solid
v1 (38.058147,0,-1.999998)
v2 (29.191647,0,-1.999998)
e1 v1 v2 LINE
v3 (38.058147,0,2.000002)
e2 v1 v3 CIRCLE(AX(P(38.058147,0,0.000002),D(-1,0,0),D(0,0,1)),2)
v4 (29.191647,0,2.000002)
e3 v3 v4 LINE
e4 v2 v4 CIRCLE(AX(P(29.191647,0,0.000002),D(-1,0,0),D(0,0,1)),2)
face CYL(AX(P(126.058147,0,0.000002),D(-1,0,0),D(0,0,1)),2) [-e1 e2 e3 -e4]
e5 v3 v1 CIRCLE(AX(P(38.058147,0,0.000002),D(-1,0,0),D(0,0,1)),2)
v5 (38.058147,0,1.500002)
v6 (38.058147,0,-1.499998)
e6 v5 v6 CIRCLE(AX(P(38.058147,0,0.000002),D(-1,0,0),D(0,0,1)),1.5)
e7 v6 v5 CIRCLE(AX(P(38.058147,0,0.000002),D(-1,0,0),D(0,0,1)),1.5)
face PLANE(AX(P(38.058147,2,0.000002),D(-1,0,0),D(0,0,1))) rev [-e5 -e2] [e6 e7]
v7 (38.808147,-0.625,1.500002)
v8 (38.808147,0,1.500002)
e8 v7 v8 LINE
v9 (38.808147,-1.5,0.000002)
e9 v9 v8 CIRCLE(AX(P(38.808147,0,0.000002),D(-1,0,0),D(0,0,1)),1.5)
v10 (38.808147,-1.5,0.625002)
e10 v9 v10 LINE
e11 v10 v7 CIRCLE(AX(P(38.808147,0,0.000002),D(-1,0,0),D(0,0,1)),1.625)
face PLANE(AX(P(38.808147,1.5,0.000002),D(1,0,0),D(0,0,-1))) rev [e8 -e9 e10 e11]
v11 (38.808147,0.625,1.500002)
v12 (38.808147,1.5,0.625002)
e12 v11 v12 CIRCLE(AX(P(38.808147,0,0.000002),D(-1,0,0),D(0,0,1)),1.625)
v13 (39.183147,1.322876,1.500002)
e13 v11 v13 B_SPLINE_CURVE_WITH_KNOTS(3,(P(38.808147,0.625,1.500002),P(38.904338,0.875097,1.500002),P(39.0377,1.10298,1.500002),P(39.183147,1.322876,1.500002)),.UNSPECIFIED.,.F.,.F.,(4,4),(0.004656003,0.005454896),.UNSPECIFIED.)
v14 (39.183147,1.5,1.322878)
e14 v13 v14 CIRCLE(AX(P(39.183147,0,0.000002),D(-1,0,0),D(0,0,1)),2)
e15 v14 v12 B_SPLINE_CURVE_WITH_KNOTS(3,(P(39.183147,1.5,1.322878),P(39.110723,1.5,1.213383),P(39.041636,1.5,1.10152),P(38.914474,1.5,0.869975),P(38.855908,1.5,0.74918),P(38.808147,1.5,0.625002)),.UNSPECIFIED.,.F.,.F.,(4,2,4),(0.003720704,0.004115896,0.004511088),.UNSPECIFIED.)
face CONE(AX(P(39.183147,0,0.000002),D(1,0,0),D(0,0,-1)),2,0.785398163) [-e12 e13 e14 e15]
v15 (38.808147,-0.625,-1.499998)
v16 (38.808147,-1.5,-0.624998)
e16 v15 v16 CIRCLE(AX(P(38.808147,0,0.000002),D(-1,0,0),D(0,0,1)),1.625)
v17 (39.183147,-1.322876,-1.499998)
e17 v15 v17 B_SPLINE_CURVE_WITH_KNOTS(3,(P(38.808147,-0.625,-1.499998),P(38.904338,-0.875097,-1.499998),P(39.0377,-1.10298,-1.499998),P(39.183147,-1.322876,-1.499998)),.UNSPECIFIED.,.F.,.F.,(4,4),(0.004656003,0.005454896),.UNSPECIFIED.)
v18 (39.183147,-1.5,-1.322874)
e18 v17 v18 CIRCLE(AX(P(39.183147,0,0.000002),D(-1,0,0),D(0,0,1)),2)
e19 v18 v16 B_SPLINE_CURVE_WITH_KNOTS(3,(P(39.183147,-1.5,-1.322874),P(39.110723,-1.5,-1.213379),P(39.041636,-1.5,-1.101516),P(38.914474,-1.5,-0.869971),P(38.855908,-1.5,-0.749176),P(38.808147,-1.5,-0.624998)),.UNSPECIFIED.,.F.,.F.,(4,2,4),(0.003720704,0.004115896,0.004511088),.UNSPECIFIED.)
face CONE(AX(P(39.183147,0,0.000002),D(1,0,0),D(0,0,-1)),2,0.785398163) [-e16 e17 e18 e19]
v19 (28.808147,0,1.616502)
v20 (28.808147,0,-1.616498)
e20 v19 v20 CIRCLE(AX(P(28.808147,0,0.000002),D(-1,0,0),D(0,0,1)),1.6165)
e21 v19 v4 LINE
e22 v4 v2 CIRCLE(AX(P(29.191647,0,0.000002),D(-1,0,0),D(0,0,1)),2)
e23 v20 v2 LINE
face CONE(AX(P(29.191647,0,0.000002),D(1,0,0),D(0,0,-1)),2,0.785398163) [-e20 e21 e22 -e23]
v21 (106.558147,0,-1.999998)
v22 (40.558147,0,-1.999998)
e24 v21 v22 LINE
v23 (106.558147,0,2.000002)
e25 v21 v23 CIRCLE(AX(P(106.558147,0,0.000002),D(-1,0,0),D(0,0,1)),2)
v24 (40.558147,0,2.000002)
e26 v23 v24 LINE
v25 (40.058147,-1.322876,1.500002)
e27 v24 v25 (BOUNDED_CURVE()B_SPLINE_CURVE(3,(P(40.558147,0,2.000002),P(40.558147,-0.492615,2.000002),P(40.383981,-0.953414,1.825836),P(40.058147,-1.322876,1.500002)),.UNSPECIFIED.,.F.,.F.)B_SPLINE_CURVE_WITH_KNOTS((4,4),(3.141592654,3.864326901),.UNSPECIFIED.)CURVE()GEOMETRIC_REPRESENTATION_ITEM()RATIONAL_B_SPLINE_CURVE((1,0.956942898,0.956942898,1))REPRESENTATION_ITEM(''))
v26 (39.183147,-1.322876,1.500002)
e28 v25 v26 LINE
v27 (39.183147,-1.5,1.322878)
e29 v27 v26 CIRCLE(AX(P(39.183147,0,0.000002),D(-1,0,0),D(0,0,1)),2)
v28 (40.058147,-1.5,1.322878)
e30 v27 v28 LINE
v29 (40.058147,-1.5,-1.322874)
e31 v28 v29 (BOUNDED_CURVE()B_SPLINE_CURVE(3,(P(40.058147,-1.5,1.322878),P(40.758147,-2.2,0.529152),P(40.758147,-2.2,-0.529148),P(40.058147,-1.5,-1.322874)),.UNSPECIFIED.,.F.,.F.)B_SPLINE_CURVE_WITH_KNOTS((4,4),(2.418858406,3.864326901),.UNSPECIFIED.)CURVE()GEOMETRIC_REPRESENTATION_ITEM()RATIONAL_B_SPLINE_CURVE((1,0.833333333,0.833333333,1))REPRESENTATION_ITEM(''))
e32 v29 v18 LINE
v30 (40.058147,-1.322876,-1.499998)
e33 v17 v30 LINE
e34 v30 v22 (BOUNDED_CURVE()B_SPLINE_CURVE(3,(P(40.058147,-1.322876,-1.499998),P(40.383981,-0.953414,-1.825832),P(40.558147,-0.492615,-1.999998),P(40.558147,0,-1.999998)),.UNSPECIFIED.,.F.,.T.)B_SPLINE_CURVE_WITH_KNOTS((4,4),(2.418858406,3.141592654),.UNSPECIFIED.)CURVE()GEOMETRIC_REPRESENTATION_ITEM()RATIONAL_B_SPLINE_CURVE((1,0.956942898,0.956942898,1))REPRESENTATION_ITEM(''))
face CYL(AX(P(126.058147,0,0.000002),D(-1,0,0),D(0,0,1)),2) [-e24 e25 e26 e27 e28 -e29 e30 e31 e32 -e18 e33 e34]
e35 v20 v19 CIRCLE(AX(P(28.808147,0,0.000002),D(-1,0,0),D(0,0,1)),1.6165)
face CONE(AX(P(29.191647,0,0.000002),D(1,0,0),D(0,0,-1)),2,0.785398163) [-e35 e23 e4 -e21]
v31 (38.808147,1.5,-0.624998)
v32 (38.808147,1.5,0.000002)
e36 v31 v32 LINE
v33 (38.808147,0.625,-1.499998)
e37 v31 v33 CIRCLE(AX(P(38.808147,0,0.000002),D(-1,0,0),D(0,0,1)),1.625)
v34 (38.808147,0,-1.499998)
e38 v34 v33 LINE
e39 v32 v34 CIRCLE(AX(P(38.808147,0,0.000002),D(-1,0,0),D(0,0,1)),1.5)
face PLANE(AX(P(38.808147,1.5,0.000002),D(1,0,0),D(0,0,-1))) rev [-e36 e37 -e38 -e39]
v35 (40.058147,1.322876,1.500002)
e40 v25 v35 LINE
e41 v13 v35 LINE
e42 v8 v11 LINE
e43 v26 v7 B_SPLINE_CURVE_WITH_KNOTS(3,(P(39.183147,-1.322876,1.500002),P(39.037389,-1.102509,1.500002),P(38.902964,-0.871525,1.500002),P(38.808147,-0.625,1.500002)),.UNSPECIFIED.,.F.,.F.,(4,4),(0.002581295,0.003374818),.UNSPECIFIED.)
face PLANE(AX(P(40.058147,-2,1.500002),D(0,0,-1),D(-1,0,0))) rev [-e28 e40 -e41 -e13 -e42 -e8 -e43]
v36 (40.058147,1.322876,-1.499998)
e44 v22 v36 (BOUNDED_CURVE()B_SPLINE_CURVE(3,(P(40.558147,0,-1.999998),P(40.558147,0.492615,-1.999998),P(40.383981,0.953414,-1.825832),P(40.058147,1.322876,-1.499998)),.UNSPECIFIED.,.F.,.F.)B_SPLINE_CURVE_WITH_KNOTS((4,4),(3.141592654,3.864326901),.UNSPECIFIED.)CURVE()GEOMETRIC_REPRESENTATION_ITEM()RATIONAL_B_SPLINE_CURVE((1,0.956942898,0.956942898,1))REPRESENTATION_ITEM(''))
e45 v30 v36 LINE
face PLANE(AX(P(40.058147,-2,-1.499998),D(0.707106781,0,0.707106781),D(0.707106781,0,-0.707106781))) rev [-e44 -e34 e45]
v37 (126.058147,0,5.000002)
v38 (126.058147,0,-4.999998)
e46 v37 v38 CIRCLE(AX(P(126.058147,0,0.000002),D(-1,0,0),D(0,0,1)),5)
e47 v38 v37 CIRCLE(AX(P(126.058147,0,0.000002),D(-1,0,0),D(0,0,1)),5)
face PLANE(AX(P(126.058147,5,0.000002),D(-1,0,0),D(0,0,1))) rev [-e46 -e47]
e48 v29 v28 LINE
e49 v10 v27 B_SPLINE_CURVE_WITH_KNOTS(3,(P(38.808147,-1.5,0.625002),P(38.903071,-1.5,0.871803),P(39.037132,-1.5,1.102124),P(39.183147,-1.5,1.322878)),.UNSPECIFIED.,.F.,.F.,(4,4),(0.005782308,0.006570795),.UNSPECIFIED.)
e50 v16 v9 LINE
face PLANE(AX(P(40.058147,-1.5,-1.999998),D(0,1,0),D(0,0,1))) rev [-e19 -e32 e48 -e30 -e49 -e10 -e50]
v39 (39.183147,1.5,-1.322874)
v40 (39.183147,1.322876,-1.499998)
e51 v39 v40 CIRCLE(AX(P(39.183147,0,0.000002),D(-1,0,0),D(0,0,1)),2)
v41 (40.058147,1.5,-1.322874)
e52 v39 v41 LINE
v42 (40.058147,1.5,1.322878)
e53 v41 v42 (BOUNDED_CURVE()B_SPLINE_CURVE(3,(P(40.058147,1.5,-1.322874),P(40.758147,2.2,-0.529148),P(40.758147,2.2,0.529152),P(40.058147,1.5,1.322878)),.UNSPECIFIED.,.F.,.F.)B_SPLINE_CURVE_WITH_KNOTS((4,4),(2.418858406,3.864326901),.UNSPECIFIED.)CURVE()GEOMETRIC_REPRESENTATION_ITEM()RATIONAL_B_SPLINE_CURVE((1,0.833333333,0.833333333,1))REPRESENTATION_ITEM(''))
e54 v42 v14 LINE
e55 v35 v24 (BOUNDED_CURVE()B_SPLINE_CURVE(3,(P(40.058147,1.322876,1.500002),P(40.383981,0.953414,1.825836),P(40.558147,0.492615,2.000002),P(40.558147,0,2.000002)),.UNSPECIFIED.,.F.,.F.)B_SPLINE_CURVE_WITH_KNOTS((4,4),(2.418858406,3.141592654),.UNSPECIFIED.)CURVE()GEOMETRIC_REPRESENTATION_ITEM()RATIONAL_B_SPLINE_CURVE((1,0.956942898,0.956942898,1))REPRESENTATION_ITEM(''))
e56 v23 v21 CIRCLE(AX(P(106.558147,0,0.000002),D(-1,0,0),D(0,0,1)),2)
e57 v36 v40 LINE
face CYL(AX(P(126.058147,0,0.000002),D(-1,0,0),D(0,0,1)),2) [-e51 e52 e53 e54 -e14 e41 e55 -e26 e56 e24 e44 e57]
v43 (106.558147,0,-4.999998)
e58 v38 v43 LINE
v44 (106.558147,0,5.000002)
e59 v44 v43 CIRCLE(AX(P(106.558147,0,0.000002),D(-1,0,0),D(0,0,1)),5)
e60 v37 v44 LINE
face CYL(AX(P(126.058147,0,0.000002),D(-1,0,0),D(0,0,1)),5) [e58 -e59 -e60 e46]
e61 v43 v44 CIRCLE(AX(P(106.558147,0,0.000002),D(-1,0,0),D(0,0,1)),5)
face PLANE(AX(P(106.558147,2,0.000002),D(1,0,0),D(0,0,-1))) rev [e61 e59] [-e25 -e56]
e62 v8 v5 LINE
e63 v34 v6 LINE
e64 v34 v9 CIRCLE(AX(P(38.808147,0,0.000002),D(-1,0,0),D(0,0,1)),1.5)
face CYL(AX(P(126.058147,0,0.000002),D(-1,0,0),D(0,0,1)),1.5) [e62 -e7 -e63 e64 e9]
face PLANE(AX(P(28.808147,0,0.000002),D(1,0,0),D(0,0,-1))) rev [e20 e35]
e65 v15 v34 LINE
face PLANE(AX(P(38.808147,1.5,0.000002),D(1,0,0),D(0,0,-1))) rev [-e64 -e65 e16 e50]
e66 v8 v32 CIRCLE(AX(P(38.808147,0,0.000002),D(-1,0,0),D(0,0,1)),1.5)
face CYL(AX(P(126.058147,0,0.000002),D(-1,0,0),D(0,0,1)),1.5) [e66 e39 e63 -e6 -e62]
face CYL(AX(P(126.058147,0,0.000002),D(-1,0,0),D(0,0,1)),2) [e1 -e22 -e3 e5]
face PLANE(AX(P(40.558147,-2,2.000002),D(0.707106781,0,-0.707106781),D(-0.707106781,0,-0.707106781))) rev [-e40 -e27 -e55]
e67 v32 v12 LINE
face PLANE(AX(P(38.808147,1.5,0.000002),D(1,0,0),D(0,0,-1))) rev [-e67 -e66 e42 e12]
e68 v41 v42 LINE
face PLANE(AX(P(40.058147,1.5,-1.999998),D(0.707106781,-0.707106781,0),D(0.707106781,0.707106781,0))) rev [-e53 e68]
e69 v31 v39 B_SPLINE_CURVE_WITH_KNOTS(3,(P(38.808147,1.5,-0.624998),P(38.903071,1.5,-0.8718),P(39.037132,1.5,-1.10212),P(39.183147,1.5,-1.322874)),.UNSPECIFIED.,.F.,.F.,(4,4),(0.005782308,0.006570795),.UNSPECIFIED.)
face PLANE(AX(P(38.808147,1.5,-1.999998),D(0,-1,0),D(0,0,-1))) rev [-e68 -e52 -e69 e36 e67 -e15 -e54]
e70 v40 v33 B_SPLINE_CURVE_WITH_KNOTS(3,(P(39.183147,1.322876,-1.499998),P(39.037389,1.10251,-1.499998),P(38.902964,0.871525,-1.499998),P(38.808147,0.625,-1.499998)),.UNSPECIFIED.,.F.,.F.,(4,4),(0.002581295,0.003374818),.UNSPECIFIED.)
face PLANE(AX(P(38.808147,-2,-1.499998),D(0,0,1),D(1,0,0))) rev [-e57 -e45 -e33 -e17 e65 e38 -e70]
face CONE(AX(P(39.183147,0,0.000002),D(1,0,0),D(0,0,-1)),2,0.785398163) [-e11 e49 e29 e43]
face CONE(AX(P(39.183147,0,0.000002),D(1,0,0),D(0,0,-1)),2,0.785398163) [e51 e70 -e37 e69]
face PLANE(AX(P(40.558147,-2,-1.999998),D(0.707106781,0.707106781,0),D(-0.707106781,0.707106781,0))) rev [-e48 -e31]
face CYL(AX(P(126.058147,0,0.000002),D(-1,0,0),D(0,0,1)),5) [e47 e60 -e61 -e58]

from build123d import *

# Parameters (mm, degrees)
CUT_EXTRUDE_1_DEPTH      = 4
CUT_EXTRUDE_1_DEPTH_BACK = 4
CUT_EXTRUDE_2_DEPTH      = 4
CUT_EXTRUDE_2_DEPTH_BACK = 4
CUT_EXTRUDE_3_DEPTH      = 4
CUT_EXTRUDE_3_DEPTH_BACK = 4
CUT_EXTRUDE_4_DEPTH      = 4
CUT_EXTRUDE_4_DEPTH_BACK = 4
SCALE_1_SCALE            = 0.5


with BuildPart() as part:
    # 草图1 → 旋转1 (revolve)
    with BuildSketch(Plane.XY, mode=Mode.PRIVATE) as revolve_1_sk:
        Polygon((-40, 0), (-40, 3.233), (-39.233, 4), (-21.5, 4), (-21.5, 3), (-20, 3), (-20, 3.25), (-19.25, 4), (115.5, 4), (115.5, 10), (154.5, 10), (154.5, 0), align=None)
    revolve(revolve_1_sk.sketch.rotate(Axis((154.5, 0, 0), (-1, 0, 0)), 270), axis=Axis((154.5, 0, 0), (-1, 0, 0)))

    # 草图2 → 切除-拉伸1 (cut, two sides: drawn at the far end of the back side and taken through both)
    with BuildSketch(Plane.XY.offset(-CUT_EXTRUDE_1_DEPTH_BACK)):
        Polygon((-20, 3), (-17.5, 3), (-16.5, 4), (-20, 4), align=None)
    extrude(amount=CUT_EXTRUDE_1_DEPTH + CUT_EXTRUDE_1_DEPTH_BACK, mode=Mode.SUBTRACT)

    # 草图3 → 切除-拉伸2 (cut, two sides: drawn at the far end of the back side and taken through both)
    with BuildSketch(Plane.XY.offset(-CUT_EXTRUDE_2_DEPTH_BACK)):
        Polygon((-20, -3), (-20, -4), (-16.5, -4), (-17.5, -3), align=None)
    extrude(amount=CUT_EXTRUDE_2_DEPTH + CUT_EXTRUDE_2_DEPTH_BACK, mode=Mode.SUBTRACT)

    # 草图4 → 切除-拉伸3 (cut, two sides: drawn at the far end of the back side and taken through both)
    with BuildSketch(Plane(origin=(0, 0, 0), x_dir=(1, 0, 0), z_dir=(0, 1, 0)).offset(-CUT_EXTRUDE_3_DEPTH_BACK)):
        Polygon((-20, 3), (-17.5, 3), (-16.5, 4), (-20, 4), align=None)
    extrude(amount=CUT_EXTRUDE_3_DEPTH + CUT_EXTRUDE_3_DEPTH_BACK, mode=Mode.SUBTRACT)

    # 草图5 → 切除-拉伸4 (cut, two sides: drawn at the far end of the back side and taken through both)
    with BuildSketch(Plane(origin=(0, 0, 0), x_dir=(1, 0, 0), z_dir=(0, 1, 0)).offset(-CUT_EXTRUDE_4_DEPTH_BACK)):
        Polygon((-20, -3), (-20, -4), (-16.5, -4), (-17.5, -3), align=None)
    extrude(amount=CUT_EXTRUDE_4_DEPTH + CUT_EXTRUDE_4_DEPTH_BACK, mode=Mode.SUBTRACT)


with BuildPart() as part_1:
    # 缩放比例1: scaled about (97.615985287, 0, 0)
    add(part.part.scale(SCALE_1_SCALE).moved(Location((48.807992644, 0, 0))))


solid = part_1.part
